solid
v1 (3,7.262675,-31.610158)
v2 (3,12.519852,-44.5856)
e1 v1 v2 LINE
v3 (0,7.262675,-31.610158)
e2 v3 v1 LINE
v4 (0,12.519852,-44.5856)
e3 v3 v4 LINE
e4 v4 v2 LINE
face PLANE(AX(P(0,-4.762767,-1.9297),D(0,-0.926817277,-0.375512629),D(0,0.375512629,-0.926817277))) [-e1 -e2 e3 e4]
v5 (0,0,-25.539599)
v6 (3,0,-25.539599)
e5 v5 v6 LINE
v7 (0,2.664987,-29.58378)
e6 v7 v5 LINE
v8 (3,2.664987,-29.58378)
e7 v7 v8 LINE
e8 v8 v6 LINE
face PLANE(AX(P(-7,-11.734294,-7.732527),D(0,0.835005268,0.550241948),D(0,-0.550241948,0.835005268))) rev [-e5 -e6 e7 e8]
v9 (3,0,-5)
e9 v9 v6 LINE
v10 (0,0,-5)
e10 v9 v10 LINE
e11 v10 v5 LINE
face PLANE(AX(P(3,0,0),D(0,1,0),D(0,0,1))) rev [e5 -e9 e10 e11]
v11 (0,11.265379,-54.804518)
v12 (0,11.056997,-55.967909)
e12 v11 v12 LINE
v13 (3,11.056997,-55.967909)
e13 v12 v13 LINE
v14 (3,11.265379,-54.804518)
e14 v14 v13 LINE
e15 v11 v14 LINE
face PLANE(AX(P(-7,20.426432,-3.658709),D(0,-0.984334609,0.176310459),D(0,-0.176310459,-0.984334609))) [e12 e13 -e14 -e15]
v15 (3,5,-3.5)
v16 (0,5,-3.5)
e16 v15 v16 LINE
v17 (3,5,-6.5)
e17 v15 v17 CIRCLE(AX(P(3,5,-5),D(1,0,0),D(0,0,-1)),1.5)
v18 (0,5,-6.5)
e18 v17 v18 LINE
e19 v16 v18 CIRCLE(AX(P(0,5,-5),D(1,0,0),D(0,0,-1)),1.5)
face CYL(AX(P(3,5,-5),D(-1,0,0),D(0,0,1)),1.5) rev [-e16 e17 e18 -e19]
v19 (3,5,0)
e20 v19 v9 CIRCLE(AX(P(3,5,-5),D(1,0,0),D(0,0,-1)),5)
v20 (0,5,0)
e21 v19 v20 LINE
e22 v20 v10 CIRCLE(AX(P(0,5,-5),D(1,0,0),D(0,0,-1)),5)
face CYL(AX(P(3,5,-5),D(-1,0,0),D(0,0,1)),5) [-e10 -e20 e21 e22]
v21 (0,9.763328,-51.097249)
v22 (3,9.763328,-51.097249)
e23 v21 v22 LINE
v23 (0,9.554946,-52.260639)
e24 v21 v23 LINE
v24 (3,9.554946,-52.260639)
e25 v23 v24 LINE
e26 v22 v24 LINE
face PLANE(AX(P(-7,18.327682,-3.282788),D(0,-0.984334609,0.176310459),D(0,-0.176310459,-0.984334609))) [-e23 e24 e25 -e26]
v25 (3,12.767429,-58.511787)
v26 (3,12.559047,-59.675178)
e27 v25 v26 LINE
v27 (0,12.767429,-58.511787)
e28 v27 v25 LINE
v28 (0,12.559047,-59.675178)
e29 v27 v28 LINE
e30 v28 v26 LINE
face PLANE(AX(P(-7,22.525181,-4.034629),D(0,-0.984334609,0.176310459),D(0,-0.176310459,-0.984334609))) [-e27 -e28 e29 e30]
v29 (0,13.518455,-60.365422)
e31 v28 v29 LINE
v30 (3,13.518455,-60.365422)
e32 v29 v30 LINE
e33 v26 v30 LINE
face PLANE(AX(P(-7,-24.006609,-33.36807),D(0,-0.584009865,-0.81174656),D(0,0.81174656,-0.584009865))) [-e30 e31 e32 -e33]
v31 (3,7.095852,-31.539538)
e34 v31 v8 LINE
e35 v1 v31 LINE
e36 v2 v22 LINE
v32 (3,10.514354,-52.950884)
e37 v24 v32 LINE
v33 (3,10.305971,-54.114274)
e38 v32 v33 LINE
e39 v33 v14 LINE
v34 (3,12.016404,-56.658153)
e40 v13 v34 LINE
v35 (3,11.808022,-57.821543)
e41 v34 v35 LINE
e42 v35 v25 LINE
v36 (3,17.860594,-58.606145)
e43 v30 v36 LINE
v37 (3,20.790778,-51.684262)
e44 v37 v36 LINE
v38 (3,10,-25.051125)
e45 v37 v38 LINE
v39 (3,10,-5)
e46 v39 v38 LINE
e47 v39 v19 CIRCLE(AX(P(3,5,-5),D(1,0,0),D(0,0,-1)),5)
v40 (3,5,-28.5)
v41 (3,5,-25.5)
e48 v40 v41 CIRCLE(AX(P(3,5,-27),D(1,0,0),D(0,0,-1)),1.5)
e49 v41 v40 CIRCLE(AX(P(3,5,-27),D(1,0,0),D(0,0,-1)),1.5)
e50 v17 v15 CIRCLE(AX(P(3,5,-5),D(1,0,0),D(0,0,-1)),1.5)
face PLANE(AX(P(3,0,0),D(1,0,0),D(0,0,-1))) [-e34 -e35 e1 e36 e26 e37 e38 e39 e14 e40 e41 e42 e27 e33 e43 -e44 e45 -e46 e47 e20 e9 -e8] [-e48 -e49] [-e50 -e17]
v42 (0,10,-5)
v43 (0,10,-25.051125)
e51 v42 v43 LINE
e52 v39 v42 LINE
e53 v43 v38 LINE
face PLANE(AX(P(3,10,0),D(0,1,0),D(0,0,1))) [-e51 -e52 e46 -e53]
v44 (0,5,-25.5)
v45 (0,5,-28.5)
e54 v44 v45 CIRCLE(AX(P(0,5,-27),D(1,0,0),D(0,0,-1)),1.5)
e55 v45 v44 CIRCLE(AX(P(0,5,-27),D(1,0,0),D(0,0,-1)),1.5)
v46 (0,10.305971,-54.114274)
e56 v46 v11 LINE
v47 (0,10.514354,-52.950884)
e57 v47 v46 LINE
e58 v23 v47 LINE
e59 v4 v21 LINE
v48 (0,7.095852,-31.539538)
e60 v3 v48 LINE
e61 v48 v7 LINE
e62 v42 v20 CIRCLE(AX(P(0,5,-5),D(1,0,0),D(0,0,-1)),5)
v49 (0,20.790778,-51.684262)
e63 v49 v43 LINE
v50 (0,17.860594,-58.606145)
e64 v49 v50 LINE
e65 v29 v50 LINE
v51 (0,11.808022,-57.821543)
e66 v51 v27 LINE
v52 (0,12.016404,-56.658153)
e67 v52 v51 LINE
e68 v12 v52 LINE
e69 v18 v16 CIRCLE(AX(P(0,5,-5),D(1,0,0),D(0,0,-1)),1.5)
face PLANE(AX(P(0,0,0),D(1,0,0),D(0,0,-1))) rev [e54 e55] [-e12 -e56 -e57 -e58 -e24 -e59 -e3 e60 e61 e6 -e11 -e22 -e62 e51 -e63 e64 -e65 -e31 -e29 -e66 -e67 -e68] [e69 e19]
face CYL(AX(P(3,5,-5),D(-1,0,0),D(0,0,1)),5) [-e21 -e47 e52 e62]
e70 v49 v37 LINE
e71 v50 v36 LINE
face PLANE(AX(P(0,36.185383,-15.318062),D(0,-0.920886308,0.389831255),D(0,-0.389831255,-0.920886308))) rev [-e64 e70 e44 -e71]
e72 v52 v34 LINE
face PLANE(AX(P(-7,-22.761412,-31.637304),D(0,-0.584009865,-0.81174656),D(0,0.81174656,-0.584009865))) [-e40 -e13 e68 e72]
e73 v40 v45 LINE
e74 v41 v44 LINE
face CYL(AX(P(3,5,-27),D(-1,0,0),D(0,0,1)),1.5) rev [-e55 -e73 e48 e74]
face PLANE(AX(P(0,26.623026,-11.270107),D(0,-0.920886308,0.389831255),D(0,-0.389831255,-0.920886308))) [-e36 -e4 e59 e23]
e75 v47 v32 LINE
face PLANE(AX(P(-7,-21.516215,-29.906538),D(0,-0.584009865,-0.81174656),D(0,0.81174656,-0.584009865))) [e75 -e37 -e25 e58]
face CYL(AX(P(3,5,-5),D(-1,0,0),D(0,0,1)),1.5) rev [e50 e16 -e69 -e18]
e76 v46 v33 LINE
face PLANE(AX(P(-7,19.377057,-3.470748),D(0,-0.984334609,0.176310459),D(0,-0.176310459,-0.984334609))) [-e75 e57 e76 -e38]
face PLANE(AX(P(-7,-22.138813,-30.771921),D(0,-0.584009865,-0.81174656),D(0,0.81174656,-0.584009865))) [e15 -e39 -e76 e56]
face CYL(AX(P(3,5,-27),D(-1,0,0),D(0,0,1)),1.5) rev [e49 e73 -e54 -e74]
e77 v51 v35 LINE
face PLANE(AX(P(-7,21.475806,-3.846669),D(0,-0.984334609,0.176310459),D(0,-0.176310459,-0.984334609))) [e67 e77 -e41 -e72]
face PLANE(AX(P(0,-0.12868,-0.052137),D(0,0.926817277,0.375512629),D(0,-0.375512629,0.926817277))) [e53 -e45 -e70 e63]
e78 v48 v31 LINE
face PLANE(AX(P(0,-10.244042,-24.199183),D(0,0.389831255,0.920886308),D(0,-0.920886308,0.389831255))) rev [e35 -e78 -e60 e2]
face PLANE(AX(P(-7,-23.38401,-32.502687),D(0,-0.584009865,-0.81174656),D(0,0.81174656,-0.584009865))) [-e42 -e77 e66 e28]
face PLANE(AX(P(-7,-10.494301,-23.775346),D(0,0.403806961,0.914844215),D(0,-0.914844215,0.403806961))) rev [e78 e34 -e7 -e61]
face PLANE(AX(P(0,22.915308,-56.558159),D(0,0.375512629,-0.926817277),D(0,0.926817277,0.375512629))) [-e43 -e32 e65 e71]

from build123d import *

# Parameters (mm, degrees)
SKETCH1_R           = 5
SKETCH1_R_2         = 1.5
BOSS_EXTRUDE1_DEPTH = 3
BOSS_EXTRUDE2_START = -3
BOSS_EXTRUDE2_DEPTH = 3
CUT_EXTRUDE2_DEPTH  = 65.81382707
CUT_EXTRUDE3_START  = -10
CUT_EXTRUDE3_DEPTH  = 10


with BuildPart() as part:
    # Sketch1 → Boss-Extrude1 (new body)
    # profile 1 of 3: a face of its own
    with BuildSketch(Plane(origin=(0, 0, 0), x_dir=(0, 0, -1), z_dir=(1, 0, 0))):
        with Locations((5, 5)):
            Circle(SKETCH1_R)
        with Locations((5, 5)):
            Circle(SKETCH1_R_2, mode=Mode.SUBTRACT)
    # profile 2 of 3: a face of its own
    with BuildSketch(Plane(origin=(0, 0, 0), x_dir=(0, 0, -1), z_dir=(1, 0, 0))):
        with BuildLine():
            ThreePointArc((10, 5), (8.535533906, 1.464466094), (5, 0))
            Line((5, 0), (27, 0))
            ThreePointArc((27, 0), (22, 5), (27, 10))
            Line((27, 10), (5, 10))
            ThreePointArc((5, 10), (8.535533906, 8.535533906), (10, 5))
        make_face()
    # profile 3 of 3: a face of its own
    with BuildSketch(Plane(origin=(0, 0, 0), x_dir=(0, 0, -1), z_dir=(1, 0, 0))):
        with Locations((27, 5)):
            Circle(SKETCH1_R)
        with Locations((27, 5)):
            Circle(SKETCH1_R_2, mode=Mode.SUBTRACT)
    extrude(amount=BOSS_EXTRUDE1_DEPTH)

    # Sketch2 → Boss-Extrude2 (add)
    with BuildSketch(Plane(origin=(3, 0, 0), x_dir=(0, 0, -1), z_dir=(1, 0, 0)).offset(BOSS_EXTRUDE2_START)):
        with BuildLine():
            ThreePointArc((27, 10), (29.694507461, 9.21184396), (31.53953799, 7.095851816))
            Line((31.53953799, 7.095851816), (31.610157793, 7.262674791))
            Line((31.610157793, 7.262674791), (44.585599673, 12.519851602))
            Line((44.585599673, 12.519851602), (51.097249205, 9.763328363))
            Line((51.097249205, 9.763328363), (60.365421977, 13.518454657))
            Line((60.365421977, 13.518454657), (56.610295683, 22.786627428))
            Line((56.610295683, 22.786627428), (25.051124858, 10))
            Line((25.051124858, 10), (27, 10))
        make_face()
        Polygon((60.365421977, 13.518454657), (51.097249205, 9.763328363), (51.333822162, 9.179433479), (60.601994933, 12.934559772), align=None)
    extrude(amount=BOSS_EXTRUDE2_DEPTH)

    # Sketch4 → Cut-Extrude2 (cut, through all)
    with BuildSketch(Plane(origin=(3, 0, 0), x_dir=(0, 0, -1), z_dir=(1, 0, 0))):
        Polygon((56.610295683, 22.786627428), (51.684261855, 20.790777803), (58.606145308, 17.8605936), align=None)
    extrude(amount=-CUT_EXTRUDE2_DEPTH, mode=Mode.SUBTRACT)

    # Sketch5 → Cut-Extrude3 (cut)
    with BuildSketch(Plane(origin=(3, 0, 0), x_dir=(0, 0, -1), z_dir=(1, 0, 0)).offset(CUT_EXTRUDE3_START)):
        with BuildLine():
            ThreePointArc((27, 0), (31.21184396, 2.305492539), (31.53953799, 7.095851816))
            Line((31.53953799, 7.095851816), (29.583779735, 2.664986829))
            Line((29.583779735, 2.664986829), (25.539598719, 0))
            Line((25.539598719, 0), (27, 0))
        make_face()
        Polygon((52.260639439, 9.554946108), (51.097249205, 9.763328363), (51.333822162, 9.179433479), align=None)
        Polygon((52.95088376, 10.514353622), (52.260639439, 9.554946108), (54.114273993, 10.305971367), align=None)
        Polygon((54.804518314, 11.265378881), (54.114273993, 10.305971367), (55.967908548, 11.056996626), align=None)
        Polygon((56.658152868, 12.01640414), (55.967908548, 11.056996626), (57.821543102, 11.808021884), align=None)
        Polygon((58.511787422, 12.767429398), (57.821543102, 11.808021884), (59.675177656, 12.559047143), align=None)
        Polygon((60.365421977, 13.518454657), (59.675177656, 12.559047143), (60.601994933, 12.934559772), align=None)
    extrude(amount=CUT_EXTRUDE3_DEPTH, mode=Mode.SUBTRACT)


solid = part.part
